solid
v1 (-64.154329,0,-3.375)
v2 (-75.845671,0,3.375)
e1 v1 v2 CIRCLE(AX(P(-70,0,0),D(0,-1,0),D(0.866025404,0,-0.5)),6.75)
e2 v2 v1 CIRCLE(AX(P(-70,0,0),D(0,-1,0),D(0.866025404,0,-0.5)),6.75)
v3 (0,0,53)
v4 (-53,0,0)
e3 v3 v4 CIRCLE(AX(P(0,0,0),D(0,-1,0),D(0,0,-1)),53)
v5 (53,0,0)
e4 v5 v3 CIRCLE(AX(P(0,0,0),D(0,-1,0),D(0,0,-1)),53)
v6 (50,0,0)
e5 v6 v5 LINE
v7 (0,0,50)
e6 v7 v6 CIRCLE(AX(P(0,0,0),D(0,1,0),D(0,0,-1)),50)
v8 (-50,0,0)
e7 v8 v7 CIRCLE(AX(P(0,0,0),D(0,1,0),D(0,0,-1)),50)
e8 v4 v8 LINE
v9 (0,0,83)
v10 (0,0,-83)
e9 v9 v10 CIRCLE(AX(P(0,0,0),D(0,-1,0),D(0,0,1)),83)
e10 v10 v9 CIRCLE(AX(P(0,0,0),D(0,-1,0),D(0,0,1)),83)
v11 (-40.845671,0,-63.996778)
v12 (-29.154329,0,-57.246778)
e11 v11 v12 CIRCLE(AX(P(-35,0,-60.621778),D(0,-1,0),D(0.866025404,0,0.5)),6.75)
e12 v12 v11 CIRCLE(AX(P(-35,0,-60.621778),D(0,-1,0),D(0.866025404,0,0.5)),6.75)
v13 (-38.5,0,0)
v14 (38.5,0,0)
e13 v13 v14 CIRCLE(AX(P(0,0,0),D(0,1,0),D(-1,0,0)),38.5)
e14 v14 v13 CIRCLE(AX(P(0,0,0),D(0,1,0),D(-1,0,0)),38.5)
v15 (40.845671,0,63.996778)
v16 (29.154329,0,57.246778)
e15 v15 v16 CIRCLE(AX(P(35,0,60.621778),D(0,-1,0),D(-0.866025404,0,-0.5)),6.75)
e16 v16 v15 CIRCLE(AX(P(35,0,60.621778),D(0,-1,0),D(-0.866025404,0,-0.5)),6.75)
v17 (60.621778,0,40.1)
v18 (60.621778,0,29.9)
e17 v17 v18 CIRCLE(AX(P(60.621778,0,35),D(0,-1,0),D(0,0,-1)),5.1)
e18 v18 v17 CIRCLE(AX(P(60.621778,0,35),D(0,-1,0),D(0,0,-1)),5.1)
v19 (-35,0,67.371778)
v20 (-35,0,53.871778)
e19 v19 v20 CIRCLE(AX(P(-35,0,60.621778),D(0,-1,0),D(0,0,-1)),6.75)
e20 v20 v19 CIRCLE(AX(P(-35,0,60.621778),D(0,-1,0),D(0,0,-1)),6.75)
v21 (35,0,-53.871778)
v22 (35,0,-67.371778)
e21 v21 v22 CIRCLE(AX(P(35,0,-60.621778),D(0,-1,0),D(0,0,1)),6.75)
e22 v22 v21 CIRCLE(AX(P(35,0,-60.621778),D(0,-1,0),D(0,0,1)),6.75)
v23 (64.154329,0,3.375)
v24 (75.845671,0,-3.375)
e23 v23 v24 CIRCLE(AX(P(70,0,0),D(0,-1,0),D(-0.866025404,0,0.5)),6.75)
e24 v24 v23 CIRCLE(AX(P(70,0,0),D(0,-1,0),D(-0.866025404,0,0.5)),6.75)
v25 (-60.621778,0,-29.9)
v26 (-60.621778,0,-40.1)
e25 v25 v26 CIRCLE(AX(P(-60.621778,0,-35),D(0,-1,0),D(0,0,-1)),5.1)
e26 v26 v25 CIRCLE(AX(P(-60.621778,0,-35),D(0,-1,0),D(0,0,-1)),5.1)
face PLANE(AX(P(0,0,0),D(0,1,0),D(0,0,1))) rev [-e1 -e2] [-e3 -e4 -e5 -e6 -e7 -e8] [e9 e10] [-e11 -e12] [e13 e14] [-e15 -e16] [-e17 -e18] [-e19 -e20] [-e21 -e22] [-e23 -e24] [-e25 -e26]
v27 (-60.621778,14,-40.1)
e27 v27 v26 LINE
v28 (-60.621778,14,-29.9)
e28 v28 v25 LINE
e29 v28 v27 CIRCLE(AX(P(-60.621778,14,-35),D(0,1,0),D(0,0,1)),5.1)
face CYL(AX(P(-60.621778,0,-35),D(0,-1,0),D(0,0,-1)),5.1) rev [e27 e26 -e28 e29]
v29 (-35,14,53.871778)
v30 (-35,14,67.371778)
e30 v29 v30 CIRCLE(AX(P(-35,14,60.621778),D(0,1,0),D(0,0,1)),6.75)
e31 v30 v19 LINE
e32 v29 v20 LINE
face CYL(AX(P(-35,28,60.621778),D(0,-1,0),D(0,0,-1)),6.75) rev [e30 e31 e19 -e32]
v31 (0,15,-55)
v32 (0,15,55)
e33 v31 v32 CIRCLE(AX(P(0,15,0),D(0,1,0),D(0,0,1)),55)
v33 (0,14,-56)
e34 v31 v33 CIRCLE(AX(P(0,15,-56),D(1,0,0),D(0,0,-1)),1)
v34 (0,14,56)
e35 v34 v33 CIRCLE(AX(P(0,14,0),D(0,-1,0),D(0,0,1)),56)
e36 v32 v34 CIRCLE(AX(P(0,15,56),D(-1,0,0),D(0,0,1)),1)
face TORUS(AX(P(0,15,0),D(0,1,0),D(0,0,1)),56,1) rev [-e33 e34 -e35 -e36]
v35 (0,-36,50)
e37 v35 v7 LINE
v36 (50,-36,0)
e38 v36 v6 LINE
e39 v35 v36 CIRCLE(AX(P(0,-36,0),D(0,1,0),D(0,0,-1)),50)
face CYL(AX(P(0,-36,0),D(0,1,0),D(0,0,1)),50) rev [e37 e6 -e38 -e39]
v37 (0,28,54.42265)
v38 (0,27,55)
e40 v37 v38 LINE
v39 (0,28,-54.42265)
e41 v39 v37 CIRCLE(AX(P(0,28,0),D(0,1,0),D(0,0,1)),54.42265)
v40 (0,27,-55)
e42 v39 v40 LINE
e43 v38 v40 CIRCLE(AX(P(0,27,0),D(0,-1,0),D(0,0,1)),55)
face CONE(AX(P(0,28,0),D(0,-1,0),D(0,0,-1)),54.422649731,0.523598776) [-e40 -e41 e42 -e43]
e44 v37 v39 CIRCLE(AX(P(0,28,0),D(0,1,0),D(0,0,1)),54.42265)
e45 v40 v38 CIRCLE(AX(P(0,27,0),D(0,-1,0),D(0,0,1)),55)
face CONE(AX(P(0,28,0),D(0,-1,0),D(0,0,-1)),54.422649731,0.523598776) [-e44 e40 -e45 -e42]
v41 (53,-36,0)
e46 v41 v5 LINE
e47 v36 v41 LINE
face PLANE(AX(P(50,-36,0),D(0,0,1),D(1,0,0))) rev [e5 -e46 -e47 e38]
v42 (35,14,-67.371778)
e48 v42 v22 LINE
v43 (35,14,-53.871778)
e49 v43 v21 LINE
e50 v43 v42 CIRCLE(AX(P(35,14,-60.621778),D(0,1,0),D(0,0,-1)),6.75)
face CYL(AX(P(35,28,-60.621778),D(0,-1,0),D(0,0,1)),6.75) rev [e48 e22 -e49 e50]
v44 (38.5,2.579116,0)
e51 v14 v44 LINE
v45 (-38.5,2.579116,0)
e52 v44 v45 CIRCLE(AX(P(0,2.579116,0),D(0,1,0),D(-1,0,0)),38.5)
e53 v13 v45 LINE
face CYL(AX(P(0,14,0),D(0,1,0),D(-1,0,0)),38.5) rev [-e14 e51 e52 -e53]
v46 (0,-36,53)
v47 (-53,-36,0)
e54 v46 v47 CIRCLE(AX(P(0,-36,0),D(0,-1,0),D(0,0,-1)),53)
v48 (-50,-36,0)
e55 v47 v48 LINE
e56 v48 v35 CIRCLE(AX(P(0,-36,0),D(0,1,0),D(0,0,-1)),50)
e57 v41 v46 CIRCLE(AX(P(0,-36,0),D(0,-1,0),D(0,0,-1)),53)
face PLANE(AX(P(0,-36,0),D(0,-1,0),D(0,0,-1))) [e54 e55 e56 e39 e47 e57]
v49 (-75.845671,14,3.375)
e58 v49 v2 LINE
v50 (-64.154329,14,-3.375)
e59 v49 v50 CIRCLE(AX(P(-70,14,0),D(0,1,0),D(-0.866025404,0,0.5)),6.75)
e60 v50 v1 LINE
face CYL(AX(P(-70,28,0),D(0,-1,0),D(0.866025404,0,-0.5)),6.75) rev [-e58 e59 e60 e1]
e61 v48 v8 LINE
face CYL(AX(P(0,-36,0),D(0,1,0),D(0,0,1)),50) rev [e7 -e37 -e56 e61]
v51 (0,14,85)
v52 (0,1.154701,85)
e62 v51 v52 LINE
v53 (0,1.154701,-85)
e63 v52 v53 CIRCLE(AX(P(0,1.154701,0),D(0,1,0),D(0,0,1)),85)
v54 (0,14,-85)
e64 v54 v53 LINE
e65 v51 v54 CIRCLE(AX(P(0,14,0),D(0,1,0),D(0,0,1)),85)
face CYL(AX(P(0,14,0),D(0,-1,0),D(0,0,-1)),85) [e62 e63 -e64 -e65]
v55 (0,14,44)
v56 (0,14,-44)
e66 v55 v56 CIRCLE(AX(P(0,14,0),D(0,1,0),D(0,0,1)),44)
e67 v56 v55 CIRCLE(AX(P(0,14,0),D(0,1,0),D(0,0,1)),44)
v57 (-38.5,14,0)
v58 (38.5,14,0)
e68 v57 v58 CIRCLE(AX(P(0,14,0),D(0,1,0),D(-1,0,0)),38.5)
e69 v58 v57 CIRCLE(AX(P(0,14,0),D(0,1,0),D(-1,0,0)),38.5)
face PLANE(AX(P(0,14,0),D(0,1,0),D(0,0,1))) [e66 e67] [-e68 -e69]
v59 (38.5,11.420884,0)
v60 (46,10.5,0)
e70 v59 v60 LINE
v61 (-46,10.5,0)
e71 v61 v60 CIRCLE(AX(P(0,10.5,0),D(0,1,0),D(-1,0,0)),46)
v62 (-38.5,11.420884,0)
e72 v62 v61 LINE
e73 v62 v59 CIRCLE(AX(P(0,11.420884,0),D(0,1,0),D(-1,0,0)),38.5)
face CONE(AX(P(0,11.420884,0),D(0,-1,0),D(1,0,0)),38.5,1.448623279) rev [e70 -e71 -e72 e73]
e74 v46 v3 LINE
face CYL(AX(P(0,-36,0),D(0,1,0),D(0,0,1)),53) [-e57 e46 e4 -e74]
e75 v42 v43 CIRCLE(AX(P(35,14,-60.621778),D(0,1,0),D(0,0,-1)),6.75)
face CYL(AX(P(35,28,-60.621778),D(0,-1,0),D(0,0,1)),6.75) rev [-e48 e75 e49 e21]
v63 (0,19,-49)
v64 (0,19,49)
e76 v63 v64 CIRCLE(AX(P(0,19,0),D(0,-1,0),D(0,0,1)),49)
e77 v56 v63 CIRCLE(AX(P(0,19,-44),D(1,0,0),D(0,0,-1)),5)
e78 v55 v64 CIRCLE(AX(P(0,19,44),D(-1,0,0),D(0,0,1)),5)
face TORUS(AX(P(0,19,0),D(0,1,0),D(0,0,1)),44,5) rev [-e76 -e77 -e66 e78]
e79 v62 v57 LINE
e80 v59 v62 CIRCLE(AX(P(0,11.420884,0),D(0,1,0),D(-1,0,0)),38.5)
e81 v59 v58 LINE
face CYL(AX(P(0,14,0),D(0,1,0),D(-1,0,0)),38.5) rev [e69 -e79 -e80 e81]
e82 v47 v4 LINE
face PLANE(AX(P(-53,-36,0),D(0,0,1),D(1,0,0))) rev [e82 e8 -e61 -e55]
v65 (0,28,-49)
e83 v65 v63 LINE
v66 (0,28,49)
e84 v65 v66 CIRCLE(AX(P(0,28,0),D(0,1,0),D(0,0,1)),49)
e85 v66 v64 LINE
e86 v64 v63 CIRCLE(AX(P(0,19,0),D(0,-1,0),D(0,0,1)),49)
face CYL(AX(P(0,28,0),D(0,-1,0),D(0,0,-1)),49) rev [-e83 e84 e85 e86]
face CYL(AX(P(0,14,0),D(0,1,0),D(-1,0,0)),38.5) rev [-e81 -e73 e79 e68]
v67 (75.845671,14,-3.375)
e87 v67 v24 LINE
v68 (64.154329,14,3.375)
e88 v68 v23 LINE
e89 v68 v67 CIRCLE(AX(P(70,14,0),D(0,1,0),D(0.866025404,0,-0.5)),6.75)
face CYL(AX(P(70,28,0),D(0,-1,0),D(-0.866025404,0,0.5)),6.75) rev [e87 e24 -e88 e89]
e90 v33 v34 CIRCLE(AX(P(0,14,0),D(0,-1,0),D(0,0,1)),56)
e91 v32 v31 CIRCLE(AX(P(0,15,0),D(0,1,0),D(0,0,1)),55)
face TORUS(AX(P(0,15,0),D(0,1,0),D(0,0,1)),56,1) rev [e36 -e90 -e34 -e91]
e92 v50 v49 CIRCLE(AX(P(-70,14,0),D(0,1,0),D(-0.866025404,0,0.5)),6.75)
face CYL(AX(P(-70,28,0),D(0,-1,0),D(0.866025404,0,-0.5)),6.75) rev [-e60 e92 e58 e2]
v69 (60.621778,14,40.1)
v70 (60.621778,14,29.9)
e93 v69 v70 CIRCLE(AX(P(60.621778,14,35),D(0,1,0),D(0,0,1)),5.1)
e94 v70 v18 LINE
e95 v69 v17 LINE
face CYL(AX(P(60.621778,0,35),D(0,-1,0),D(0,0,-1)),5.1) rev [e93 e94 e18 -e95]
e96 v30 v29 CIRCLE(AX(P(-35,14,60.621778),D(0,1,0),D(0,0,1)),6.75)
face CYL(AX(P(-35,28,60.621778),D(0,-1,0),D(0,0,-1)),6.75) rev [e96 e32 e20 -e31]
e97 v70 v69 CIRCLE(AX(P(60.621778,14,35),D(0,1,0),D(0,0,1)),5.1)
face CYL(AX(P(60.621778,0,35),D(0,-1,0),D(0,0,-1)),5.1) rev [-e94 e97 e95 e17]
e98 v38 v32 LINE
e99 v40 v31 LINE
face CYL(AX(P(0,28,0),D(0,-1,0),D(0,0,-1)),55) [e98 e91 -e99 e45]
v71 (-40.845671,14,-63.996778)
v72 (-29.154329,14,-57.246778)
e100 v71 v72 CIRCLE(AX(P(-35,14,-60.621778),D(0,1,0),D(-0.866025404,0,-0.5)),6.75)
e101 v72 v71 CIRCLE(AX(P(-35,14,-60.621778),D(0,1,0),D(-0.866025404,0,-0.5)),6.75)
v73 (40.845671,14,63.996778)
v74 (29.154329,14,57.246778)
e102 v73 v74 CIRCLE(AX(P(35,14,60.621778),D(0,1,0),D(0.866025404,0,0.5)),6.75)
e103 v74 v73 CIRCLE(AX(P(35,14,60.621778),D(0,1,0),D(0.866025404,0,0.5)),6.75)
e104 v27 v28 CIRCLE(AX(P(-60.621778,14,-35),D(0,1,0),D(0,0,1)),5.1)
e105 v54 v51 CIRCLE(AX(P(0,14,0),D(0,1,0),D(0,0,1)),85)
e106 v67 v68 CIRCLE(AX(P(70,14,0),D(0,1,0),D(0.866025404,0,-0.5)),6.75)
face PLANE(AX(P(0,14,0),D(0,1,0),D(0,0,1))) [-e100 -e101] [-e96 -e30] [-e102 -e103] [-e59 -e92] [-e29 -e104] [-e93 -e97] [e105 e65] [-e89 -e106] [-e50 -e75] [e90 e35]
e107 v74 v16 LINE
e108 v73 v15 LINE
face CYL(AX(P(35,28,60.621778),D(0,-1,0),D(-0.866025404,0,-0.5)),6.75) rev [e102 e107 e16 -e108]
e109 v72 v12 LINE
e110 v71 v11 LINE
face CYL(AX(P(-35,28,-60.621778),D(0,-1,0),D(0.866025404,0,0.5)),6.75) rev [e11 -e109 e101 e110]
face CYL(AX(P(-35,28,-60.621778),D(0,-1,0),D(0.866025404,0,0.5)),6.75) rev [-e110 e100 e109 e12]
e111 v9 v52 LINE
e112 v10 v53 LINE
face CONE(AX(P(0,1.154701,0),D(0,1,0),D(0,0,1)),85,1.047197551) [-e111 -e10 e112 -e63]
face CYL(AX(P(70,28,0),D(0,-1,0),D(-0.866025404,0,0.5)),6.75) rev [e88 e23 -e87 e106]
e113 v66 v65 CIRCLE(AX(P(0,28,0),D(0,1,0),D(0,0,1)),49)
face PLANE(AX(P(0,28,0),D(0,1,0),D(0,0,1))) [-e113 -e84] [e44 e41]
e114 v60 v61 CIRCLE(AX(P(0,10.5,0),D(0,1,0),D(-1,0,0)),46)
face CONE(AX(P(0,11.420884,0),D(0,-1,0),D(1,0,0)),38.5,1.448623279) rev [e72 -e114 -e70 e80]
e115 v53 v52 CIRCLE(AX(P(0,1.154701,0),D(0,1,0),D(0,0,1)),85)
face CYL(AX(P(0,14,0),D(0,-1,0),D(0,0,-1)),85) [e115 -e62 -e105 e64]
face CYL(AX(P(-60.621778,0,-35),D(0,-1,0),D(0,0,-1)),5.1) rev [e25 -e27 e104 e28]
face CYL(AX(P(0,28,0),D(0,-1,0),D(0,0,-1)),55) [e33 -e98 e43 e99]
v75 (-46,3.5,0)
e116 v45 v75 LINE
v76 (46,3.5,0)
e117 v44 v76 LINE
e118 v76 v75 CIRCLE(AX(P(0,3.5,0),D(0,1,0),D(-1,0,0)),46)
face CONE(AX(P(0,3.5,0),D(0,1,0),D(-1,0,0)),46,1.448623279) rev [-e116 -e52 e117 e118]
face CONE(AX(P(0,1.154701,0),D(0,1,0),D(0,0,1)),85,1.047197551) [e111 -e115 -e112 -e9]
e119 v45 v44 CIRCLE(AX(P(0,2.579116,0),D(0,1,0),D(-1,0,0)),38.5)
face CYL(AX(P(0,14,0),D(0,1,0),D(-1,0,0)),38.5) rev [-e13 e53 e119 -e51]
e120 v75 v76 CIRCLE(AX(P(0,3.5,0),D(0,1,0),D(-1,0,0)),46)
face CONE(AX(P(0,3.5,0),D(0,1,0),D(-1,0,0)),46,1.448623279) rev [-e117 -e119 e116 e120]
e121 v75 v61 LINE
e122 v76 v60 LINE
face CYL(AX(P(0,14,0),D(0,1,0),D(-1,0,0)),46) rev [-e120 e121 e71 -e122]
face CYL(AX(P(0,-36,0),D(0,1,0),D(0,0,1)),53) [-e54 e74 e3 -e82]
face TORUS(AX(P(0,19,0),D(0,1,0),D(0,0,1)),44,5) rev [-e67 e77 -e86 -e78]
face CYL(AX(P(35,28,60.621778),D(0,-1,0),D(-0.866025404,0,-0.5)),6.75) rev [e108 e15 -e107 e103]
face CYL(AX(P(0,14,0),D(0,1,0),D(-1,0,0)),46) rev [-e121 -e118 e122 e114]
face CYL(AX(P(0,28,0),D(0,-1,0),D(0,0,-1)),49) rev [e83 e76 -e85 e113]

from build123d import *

# Parameters (mm, degrees)
SKETCH1_R           = 85
BOSS_EXTRUDE1_DEPTH = 14
SKETCH2_R           = 55
SKETCH2_R_2         = 49
BOSS_EXTRUDE2_DEPTH = 14
FILLET1_R           = 5
FILLET2_R           = 1
CHAMFER1_SIZE       = 2
CHAMFER1_SIZE2      = 1.154700538
CHAMFER2_SIZE       = 1
CHAMFER2_SIZE2      = 0.577350269
BOSS_EXTRUDE3_DEPTH = 36
SKETCH5_R           = 6.75
CUT_EXTRUDE1_DEPTH  = 126.483066587
CIRPATTERN1_COUNT   = 6
M12_TAPPED_HOLE1_D  = 10.2


with BuildPart() as part:
    # Sketch1 → Boss-Extrude1 (new body)
    with BuildSketch(Plane(origin=(0, 0, 0), x_dir=(1, 0, 0), z_dir=(0, 1, 0))):
        with Locations(Location((0, 0, 0), (0, 0, 270))):
            Circle(SKETCH1_R)
    extrude(amount=BOSS_EXTRUDE1_DEPTH)

    # Sketch2 → Boss-Extrude2 (add)
    with BuildSketch(Plane(origin=(0, 14, 0), x_dir=(1, 0, 0), z_dir=(0, 1, 0))):
        with Locations(Location((0, 0, 0), (0, 0, 270))):
            Circle(SKETCH2_R)
        with Locations(Location((0, 0, 0), (0, 0, 270))):
            Circle(SKETCH2_R_2, mode=Mode.SUBTRACT)
    extrude(amount=BOSS_EXTRUDE2_DEPTH)

    # Fillet1
    fillet1_edges = [part.edges().sort_by_distance(p)[0] for p in [
        (0, 14, -49),
    ]]
    fillet(fillet1_edges, radius=FILLET1_R)

    # Fillet2
    fillet2_edges = [part.edges().sort_by_distance(p)[0] for p in [
        (0, 14, -55),
    ]]
    fillet(fillet2_edges, radius=FILLET2_R)

    # Chamfer1
    chamfer1_edges = [part.edges().sort_by_distance(p)[0] for p in [
        (0, 0, -85),
    ]]
    chamfer1_side = [part.faces().sort_by_distance(p)[0] for p in [
        (0, 0, 0),
    ]]
    chamfer(chamfer1_edges, length=CHAMFER1_SIZE, length2=CHAMFER1_SIZE2, reference=chamfer1_side[0])

    # Chamfer2
    chamfer2_edges = [part.edges().sort_by_distance(p)[0] for p in [
        (0, 28, -55),
    ]]
    chamfer2_side = [part.faces().sort_by_distance(p)[0] for p in [
        (0, 21.5, -55),
    ]]
    chamfer(chamfer2_edges, length=CHAMFER2_SIZE, length2=CHAMFER2_SIZE2, reference=chamfer2_side[0])

    # Sketch3 → Boss-Extrude3 (add)
    with BuildSketch(Plane.XZ):
        with BuildLine():
            Line((-53, 0), (-50, 0))
            ThreePointArc((-50, 0), (0, 50), (50, 0))
            Line((50, 0), (53, 0))
            ThreePointArc((53, 0), (0, 53), (-53, 0))
        make_face()
    extrude(amount=BOSS_EXTRUDE3_DEPTH)

    # Sketch4 → Cut-Revolve1 (revolve, cut)
    with BuildSketch(Plane.XY):
        Polygon((-46, 10.5), (-46, 3.5), (-38.5, 2.579115793), (-38.5, 0), (0, 0), (0, 14), (-38.5, 14), (-38.5, 11.420884207), align=None)
    revolve(axis=Axis((0, 14, 0), (0, -1, 0)), mode=Mode.SUBTRACT)

    # Sketch5 → Cut-Extrude1 (cut, through all)
    with BuildSketch(Plane.XZ):
        with Locations(Location((-35, 60.621778265, 0), (0, 0, 270))):
            Circle(SKETCH5_R)
    cut_extrude1 = extrude(amount=-CUT_EXTRUDE1_DEPTH, mode=Mode.SUBTRACT)

    # CirPattern1: Cut-Extrude1 ×6 about axis
    cirpattern1_axis = Axis((0, 0, 0), (0, 1, 0))
    for i in range(1, CIRPATTERN1_COUNT):
        add(cut_extrude1.rotate(cirpattern1_axis, i * 360 / CIRPATTERN1_COUNT), mode=Mode.SUBTRACT)

    # M12 Tapped Hole1 (through all)
    with Locations(Plane(origin=(0, 0, 0), x_dir=(-1, 0, 0), z_dir=(0, -1, 0))):
        with Locations((-60.621778265, -35), (60.621778265, 35)):
            Hole(M12_TAPPED_HOLE1_D / 2)


solid = part.part
